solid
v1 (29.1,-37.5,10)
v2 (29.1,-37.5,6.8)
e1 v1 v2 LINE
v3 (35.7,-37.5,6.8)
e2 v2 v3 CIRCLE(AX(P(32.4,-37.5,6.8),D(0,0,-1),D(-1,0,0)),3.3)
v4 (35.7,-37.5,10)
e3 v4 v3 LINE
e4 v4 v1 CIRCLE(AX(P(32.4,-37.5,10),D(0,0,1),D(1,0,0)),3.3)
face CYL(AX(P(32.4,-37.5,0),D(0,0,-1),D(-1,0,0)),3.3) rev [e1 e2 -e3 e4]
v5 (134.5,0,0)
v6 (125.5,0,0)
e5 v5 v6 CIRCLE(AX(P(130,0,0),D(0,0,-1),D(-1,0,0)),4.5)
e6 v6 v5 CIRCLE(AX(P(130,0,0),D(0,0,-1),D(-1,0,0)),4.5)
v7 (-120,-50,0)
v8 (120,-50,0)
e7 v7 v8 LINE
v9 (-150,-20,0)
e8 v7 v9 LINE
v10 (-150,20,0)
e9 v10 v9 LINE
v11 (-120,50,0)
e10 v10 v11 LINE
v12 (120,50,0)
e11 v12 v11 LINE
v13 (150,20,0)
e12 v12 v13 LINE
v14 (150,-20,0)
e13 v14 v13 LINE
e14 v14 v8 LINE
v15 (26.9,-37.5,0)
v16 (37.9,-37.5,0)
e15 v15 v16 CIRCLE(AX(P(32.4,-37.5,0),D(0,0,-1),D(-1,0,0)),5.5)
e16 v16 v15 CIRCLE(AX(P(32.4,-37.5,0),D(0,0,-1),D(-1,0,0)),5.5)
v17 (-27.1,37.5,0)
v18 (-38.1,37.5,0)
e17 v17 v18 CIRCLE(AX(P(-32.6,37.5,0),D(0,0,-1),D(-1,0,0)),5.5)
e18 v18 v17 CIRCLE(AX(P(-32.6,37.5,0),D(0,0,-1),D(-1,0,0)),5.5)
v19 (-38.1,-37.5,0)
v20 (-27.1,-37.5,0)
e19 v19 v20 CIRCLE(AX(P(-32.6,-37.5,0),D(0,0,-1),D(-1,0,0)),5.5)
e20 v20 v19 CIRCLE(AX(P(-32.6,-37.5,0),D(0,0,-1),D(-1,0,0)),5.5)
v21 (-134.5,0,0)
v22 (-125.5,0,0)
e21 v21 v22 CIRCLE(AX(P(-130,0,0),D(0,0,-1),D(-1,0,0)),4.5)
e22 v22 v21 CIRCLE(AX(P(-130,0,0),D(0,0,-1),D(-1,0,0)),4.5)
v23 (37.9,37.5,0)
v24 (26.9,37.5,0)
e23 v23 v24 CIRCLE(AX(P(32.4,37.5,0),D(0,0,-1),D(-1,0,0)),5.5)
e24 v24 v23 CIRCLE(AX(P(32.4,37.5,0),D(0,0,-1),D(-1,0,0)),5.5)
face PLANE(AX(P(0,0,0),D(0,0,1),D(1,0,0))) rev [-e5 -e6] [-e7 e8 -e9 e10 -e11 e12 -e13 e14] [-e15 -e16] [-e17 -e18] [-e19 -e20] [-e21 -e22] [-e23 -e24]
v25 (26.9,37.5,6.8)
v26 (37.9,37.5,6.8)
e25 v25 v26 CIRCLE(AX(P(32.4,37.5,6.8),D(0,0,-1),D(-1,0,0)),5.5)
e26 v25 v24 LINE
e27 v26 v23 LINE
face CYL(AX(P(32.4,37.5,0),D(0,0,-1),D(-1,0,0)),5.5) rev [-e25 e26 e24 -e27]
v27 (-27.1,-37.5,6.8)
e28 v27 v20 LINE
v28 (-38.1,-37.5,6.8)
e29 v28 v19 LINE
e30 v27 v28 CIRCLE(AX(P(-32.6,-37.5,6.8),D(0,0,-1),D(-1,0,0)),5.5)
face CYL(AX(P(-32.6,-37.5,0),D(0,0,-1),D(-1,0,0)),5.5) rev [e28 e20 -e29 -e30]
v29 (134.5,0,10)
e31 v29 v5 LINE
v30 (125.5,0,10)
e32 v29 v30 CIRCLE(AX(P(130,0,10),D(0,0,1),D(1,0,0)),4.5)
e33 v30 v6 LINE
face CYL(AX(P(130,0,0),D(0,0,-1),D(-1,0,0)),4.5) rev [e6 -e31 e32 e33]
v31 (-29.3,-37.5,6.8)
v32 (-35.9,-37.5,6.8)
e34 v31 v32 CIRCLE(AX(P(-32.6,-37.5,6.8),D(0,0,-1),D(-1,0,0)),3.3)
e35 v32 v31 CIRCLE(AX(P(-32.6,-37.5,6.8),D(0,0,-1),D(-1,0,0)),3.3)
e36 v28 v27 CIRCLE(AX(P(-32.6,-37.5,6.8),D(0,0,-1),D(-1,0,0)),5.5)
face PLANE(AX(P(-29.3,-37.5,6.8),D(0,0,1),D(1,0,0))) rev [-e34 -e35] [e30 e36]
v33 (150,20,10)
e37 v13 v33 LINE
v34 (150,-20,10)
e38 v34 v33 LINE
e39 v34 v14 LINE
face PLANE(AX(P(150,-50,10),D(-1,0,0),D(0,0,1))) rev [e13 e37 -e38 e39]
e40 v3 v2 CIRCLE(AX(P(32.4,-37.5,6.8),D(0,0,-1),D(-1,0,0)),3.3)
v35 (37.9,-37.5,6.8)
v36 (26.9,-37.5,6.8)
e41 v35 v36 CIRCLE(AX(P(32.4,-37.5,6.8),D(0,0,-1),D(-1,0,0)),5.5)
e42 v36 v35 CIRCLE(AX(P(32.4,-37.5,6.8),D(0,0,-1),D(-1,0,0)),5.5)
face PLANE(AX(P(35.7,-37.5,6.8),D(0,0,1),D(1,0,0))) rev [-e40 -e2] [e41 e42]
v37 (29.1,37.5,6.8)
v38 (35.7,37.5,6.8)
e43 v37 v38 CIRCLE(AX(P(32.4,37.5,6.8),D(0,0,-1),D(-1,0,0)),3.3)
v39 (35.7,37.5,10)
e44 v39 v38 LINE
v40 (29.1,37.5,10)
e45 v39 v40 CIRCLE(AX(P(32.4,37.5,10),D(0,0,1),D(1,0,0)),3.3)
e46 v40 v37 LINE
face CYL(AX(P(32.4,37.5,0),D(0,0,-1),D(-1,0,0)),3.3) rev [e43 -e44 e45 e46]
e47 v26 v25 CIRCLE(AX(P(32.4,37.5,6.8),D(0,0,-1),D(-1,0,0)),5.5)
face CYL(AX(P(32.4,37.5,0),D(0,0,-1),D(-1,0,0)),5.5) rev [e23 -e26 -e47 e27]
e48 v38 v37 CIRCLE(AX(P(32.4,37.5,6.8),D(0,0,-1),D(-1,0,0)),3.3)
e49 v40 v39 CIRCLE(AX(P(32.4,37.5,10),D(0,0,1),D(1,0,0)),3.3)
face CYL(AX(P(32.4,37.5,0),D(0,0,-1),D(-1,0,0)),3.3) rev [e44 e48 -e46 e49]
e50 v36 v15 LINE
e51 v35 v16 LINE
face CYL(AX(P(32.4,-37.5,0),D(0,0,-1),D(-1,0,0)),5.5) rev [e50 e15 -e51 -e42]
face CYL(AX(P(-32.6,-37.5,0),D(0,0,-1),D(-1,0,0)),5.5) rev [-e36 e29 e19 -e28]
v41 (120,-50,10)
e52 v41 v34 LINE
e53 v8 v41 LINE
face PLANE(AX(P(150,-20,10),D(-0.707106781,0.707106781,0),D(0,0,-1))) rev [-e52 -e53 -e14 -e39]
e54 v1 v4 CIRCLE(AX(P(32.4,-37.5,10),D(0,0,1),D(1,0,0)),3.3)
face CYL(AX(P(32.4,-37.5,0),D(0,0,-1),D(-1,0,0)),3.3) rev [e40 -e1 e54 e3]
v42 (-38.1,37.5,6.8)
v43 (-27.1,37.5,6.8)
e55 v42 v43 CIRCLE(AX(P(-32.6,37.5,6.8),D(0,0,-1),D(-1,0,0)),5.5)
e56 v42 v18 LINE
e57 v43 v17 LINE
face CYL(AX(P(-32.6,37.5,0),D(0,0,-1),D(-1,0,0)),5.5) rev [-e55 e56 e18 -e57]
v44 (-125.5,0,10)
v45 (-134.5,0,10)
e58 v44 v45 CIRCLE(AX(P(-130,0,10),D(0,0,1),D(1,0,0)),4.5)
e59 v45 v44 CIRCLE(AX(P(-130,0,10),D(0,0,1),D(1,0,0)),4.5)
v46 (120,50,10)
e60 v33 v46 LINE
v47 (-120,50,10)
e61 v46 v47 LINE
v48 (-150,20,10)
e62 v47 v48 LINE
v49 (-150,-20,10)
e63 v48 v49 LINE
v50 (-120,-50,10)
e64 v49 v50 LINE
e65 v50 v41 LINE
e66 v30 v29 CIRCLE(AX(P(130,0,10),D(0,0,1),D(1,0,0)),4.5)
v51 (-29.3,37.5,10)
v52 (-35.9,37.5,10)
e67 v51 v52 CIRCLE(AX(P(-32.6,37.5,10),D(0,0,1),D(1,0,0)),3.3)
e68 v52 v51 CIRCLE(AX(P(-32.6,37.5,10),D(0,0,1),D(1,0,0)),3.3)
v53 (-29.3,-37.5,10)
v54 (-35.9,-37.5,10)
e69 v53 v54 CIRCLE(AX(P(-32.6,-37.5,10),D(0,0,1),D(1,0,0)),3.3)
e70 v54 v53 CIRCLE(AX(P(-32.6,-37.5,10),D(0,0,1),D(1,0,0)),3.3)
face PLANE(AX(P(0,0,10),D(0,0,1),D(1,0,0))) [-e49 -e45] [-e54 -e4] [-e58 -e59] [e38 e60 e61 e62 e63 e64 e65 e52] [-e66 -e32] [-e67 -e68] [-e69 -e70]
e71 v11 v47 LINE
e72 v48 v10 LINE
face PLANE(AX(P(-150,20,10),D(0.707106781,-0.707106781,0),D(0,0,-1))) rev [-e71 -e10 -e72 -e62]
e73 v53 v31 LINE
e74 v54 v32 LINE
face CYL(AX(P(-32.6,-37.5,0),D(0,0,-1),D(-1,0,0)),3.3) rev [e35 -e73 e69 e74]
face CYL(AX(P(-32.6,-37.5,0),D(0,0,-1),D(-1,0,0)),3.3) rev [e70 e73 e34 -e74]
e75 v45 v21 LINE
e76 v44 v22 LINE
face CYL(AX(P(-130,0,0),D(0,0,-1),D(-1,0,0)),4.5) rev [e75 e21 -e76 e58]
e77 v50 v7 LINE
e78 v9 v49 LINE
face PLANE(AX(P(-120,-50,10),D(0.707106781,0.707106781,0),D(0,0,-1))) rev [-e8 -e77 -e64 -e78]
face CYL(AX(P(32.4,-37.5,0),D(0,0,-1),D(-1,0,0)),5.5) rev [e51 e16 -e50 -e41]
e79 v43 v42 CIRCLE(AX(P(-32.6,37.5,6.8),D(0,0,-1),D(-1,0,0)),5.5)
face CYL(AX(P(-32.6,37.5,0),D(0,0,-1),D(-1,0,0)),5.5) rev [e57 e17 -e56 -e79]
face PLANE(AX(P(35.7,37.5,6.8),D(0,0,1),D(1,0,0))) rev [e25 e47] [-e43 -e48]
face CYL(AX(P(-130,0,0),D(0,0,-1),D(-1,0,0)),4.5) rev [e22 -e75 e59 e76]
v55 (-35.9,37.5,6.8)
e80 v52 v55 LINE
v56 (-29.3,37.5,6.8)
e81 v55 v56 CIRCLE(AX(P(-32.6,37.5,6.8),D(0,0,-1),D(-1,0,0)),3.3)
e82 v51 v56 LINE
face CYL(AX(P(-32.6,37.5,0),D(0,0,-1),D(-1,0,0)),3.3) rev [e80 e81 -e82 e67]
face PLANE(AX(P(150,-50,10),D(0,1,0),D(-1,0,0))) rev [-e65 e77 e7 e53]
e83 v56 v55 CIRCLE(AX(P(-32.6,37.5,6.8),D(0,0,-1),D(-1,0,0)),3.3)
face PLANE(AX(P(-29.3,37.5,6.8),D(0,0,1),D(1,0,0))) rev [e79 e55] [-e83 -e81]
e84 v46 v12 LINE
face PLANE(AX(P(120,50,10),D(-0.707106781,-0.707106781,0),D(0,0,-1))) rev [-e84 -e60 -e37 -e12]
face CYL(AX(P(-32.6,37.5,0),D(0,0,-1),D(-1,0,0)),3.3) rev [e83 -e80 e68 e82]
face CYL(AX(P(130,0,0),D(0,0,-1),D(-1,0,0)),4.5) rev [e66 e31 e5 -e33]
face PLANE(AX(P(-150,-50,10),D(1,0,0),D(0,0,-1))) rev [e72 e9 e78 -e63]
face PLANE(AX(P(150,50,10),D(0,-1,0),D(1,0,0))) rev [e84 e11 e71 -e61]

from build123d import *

# Parameters (mm, degrees)
SKETCH_1_W                = 300
SKETCH_1_H                = 100
EXTRUDE_1_DEPTH           = 10
HOLE_WIZARD_1_D           = 6.6
HOLE_WIZARD_1_CBORE_D     = 11
HOLE_WIZARD_1_CBORE_DEPTH = 6.8
HOLE_WIZARD_M8_1_D        = 9
CHAMFER_1_SIZE            = 30


with BuildPart() as part:
    # 草图1 → 凸台-拉伸1 (new body)
    with BuildSketch(Plane.XY):
        Rectangle(SKETCH_1_W, SKETCH_1_H)
    extrude(amount=EXTRUDE_1_DEPTH)

    # 打孔尺寸(%根据)内六角圆柱头螺钉的类型1 (through all)
    with Locations(Plane(origin=(0, 0, 0), x_dir=(-1, 0, 0), z_dir=(0, 0, -1))):
        with Locations((32.599999971, -37.5), (-32.400000029, -37.5), (-32.400000029, 37.5), (32.599999971, 37.5)):
            CounterBoreHole(HOLE_WIZARD_1_D / 2, HOLE_WIZARD_1_CBORE_D / 2, HOLE_WIZARD_1_CBORE_DEPTH)

    # M8 间隙孔1 (through all)
    with Locations(Plane(origin=(0, 0, 0), x_dir=(-1, 0, 0), z_dir=(0, 0, -1))):
        with Locations((-130, 0), (130, 0)):
            Hole(HOLE_WIZARD_M8_1_D / 2)

    # 倒角1
    chamfer_1_edges = [part.edges().sort_by_distance(p)[0] for p in [
        (-150, 50, 5),
        (150, 50, 5),
        (150, -50, 5),
        (-150, -50, 5),
    ]]
    chamfer(chamfer_1_edges, length=CHAMFER_1_SIZE)


solid = part.part
